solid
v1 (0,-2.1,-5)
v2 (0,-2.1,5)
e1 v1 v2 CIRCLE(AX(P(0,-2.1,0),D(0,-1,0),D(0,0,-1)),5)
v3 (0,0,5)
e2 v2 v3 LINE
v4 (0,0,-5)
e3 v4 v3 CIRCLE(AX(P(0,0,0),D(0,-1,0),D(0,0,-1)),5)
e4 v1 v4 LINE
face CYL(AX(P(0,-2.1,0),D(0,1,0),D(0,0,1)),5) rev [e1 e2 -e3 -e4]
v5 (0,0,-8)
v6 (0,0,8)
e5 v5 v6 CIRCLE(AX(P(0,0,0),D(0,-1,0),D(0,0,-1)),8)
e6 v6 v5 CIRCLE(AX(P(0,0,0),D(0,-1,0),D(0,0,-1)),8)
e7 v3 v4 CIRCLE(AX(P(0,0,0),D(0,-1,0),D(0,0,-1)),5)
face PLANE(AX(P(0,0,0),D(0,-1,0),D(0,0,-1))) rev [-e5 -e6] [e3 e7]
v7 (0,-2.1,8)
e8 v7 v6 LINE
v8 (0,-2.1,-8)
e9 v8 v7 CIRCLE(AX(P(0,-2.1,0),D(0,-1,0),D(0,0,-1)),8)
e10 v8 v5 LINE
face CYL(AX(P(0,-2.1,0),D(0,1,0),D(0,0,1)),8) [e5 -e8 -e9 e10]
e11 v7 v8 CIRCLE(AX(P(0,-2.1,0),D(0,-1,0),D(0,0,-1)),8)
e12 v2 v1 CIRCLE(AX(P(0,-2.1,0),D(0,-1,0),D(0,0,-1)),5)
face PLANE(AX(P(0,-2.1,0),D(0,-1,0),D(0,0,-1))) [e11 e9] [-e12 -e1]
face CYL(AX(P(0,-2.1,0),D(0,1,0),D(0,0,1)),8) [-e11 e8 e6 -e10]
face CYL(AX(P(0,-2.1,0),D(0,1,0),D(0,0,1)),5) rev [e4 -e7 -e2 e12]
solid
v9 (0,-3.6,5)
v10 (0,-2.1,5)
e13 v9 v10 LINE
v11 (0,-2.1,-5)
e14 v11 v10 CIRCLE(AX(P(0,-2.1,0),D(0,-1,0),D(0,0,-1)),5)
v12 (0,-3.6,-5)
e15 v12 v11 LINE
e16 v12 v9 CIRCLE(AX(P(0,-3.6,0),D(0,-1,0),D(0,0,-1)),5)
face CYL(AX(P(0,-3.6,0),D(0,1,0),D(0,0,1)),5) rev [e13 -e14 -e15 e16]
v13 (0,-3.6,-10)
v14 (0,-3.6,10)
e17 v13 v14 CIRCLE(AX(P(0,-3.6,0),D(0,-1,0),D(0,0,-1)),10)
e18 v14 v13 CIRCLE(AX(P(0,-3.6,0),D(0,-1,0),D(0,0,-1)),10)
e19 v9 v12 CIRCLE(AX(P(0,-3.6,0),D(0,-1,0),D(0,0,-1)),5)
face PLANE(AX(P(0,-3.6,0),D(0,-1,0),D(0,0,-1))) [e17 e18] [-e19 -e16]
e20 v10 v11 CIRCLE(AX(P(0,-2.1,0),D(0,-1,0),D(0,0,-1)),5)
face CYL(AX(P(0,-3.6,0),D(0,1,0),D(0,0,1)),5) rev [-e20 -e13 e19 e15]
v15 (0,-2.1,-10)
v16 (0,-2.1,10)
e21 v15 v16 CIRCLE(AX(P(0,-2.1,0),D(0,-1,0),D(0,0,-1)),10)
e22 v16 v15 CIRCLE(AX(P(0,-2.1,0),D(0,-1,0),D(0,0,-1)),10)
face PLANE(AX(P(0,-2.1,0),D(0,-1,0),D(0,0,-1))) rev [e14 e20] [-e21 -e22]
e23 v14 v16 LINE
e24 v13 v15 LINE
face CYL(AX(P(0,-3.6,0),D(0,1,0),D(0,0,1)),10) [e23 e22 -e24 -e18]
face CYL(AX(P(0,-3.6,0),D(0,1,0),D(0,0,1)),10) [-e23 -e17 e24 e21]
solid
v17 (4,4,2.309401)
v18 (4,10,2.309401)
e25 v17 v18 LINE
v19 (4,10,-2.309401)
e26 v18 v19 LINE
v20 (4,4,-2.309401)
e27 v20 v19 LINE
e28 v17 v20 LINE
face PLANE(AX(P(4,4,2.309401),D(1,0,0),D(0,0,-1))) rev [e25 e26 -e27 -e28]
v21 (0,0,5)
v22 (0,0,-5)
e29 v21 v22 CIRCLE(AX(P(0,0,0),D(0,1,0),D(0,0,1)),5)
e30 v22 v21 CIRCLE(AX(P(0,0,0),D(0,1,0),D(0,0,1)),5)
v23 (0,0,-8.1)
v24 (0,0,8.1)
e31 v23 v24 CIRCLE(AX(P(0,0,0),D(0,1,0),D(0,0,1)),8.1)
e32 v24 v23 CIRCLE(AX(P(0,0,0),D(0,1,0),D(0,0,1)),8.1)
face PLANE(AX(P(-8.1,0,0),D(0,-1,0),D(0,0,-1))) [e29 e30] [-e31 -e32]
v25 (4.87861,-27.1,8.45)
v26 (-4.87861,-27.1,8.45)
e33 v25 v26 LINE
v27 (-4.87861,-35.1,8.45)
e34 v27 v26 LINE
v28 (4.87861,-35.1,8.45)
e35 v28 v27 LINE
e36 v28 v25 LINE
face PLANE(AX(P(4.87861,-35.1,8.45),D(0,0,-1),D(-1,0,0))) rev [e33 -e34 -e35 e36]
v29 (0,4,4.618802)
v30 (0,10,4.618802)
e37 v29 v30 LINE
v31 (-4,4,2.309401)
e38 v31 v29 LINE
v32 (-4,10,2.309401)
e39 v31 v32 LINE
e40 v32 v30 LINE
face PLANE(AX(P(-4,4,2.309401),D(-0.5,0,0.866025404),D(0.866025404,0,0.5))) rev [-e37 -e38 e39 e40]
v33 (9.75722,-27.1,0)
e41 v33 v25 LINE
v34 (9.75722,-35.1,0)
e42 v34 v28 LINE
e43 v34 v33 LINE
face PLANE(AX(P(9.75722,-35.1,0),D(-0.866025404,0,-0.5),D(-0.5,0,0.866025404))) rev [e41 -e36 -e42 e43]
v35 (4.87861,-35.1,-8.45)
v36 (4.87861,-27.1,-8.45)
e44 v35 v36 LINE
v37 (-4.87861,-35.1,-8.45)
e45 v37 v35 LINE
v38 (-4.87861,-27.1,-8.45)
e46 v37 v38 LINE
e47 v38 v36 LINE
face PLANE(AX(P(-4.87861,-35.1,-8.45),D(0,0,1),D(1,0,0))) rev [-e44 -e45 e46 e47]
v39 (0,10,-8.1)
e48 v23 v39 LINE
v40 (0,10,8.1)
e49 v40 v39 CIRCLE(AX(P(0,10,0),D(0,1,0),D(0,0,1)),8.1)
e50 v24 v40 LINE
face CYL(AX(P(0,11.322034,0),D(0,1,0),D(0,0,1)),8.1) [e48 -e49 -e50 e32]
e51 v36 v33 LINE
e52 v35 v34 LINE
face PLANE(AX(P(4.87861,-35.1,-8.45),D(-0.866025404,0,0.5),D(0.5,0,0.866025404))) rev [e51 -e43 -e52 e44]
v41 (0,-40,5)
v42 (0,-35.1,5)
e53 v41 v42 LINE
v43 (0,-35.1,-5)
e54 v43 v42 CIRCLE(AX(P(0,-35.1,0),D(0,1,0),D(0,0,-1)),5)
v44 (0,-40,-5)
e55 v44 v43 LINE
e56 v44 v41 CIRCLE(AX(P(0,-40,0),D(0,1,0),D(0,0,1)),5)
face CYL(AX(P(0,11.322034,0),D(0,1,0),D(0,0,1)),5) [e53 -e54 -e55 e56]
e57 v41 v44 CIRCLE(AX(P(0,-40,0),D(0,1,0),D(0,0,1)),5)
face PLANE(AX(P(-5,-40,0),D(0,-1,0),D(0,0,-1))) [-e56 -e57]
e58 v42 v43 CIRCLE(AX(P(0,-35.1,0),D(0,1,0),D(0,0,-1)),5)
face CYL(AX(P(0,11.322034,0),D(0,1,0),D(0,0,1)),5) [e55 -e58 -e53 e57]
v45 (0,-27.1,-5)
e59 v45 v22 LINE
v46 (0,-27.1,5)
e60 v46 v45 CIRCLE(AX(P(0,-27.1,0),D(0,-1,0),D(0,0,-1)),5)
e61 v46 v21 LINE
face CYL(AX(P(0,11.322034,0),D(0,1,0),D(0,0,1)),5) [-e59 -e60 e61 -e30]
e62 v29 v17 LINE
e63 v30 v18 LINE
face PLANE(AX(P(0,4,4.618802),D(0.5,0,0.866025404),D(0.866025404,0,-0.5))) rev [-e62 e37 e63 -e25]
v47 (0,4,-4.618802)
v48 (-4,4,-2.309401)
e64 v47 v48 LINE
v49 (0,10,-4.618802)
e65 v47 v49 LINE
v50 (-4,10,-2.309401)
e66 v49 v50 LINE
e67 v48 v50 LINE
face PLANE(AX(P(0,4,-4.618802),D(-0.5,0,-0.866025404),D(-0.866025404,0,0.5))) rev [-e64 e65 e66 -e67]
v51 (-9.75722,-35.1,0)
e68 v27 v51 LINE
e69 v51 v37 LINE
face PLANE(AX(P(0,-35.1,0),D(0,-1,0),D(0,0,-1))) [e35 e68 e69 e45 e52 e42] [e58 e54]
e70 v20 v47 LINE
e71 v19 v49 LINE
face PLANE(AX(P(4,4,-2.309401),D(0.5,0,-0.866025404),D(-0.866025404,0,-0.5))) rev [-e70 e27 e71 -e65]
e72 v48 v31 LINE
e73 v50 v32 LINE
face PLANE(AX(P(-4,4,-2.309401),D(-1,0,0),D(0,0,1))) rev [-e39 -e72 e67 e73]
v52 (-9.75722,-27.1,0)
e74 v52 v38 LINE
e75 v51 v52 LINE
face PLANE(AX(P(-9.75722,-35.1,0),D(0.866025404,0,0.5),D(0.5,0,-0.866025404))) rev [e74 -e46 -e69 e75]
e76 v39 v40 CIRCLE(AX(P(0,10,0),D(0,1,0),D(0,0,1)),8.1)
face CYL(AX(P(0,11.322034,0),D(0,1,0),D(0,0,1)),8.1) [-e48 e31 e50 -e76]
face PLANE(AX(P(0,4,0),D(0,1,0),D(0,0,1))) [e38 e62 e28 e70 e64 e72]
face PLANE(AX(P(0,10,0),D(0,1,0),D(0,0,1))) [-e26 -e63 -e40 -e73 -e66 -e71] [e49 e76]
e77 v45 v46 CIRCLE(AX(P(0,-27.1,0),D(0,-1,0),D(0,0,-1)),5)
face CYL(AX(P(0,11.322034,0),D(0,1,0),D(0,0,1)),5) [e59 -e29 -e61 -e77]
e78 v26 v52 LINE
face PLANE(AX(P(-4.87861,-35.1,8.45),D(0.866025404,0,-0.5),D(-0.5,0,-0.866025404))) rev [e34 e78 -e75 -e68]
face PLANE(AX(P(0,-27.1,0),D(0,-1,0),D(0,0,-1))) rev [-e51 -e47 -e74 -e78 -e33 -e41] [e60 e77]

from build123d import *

# Parameters (mm, degrees)
CUT_EXTRUDE_1_DEPTH  = 6
SKETCH_3_R           = 8
SKETCH_3_R_2         = 5
BOSS_EXTRUDE_1_DEPTH = 2.1
SKETCH_4_R           = 10
SKETCH_4_R_2         = 5
BOSS_EXTRUDE_2_DEPTH = 1.5
BOSS_EXTRUDE_START   = 8
SKETCH_5_R           = 5
BOSS_EXTRUDE_3_DEPTH = 8


with BuildPart() as part:
    # Sketch 1 → Revolve 1 (revolve)
    with BuildSketch(Plane.XY, mode=Mode.PRIVATE) as revolve_1_sk:
        Polygon((0, 10), (-8.1, 10), (-8.1, 0), (-5, 0), (-5, -40), (0, -40), align=None)
    revolve(revolve_1_sk.sketch.rotate(Axis((0, 11.322033898, 0), (0, -1, 0)), 270), axis=Axis((0, 11.322033898, 0), (0, -1, 0)))

    # Sketch 2 → Cut-Extrude 1 (cut)
    with BuildSketch(Plane(origin=(0, 10, 0), x_dir=(1, 0, 0), z_dir=(0, 1, 0))):
        Polygon((0, 4.618802154), (-4, 2.309401077), (-4, -2.309401077), (0, -4.618802154), (4, -2.309401077), (4, 2.309401077), align=None)
    extrude(amount=-CUT_EXTRUDE_1_DEPTH, mode=Mode.SUBTRACT)

    # Sketch 5 → Boss-Extrude 3 (add)
    with BuildSketch(Plane(origin=(0, -27.1, 0), x_dir=(-1, 0, 0), z_dir=(0, -1, 0)).offset(BOSS_EXTRUDE_START)):
        Polygon((-9.757219549, 0), (-4.878609775, -8.45), (4.878609775, -8.45), (9.757219549, 0), (4.878609775, 8.45), (-4.878609775, 8.45), align=None)
        with Locations(Location((0, 0, 0), (0, 0, 90))):
            Circle(SKETCH_5_R, mode=Mode.SUBTRACT)
    extrude(amount=-BOSS_EXTRUDE_3_DEPTH)


with BuildPart() as body_2:
    # Sketch 3 → Boss-Extrude 1 (new body)
    with BuildSketch(Plane.XZ):
        with Locations(Location((0, 0, 0), (0, 0, 270))):
            Circle(SKETCH_3_R)
        with Locations(Location((0, 0, 0), (0, 0, 270))):
            Circle(SKETCH_3_R_2, mode=Mode.SUBTRACT)
    extrude(amount=BOSS_EXTRUDE_1_DEPTH)


with BuildPart() as body_3:
    # Sketch 4 → Boss-Extrude 2 (new body)
    with BuildSketch(Plane.XZ.offset(2.1)):
        with Locations(Location((0, 0, 0), (0, 0, 270))):
            Circle(SKETCH_4_R)
        with Locations(Location((0, 0, 0), (0, 0, 270))):
            Circle(SKETCH_4_R_2, mode=Mode.SUBTRACT)
    extrude(amount=BOSS_EXTRUDE_2_DEPTH)


solid = Compound([part.part, body_2.part, body_3.part])
